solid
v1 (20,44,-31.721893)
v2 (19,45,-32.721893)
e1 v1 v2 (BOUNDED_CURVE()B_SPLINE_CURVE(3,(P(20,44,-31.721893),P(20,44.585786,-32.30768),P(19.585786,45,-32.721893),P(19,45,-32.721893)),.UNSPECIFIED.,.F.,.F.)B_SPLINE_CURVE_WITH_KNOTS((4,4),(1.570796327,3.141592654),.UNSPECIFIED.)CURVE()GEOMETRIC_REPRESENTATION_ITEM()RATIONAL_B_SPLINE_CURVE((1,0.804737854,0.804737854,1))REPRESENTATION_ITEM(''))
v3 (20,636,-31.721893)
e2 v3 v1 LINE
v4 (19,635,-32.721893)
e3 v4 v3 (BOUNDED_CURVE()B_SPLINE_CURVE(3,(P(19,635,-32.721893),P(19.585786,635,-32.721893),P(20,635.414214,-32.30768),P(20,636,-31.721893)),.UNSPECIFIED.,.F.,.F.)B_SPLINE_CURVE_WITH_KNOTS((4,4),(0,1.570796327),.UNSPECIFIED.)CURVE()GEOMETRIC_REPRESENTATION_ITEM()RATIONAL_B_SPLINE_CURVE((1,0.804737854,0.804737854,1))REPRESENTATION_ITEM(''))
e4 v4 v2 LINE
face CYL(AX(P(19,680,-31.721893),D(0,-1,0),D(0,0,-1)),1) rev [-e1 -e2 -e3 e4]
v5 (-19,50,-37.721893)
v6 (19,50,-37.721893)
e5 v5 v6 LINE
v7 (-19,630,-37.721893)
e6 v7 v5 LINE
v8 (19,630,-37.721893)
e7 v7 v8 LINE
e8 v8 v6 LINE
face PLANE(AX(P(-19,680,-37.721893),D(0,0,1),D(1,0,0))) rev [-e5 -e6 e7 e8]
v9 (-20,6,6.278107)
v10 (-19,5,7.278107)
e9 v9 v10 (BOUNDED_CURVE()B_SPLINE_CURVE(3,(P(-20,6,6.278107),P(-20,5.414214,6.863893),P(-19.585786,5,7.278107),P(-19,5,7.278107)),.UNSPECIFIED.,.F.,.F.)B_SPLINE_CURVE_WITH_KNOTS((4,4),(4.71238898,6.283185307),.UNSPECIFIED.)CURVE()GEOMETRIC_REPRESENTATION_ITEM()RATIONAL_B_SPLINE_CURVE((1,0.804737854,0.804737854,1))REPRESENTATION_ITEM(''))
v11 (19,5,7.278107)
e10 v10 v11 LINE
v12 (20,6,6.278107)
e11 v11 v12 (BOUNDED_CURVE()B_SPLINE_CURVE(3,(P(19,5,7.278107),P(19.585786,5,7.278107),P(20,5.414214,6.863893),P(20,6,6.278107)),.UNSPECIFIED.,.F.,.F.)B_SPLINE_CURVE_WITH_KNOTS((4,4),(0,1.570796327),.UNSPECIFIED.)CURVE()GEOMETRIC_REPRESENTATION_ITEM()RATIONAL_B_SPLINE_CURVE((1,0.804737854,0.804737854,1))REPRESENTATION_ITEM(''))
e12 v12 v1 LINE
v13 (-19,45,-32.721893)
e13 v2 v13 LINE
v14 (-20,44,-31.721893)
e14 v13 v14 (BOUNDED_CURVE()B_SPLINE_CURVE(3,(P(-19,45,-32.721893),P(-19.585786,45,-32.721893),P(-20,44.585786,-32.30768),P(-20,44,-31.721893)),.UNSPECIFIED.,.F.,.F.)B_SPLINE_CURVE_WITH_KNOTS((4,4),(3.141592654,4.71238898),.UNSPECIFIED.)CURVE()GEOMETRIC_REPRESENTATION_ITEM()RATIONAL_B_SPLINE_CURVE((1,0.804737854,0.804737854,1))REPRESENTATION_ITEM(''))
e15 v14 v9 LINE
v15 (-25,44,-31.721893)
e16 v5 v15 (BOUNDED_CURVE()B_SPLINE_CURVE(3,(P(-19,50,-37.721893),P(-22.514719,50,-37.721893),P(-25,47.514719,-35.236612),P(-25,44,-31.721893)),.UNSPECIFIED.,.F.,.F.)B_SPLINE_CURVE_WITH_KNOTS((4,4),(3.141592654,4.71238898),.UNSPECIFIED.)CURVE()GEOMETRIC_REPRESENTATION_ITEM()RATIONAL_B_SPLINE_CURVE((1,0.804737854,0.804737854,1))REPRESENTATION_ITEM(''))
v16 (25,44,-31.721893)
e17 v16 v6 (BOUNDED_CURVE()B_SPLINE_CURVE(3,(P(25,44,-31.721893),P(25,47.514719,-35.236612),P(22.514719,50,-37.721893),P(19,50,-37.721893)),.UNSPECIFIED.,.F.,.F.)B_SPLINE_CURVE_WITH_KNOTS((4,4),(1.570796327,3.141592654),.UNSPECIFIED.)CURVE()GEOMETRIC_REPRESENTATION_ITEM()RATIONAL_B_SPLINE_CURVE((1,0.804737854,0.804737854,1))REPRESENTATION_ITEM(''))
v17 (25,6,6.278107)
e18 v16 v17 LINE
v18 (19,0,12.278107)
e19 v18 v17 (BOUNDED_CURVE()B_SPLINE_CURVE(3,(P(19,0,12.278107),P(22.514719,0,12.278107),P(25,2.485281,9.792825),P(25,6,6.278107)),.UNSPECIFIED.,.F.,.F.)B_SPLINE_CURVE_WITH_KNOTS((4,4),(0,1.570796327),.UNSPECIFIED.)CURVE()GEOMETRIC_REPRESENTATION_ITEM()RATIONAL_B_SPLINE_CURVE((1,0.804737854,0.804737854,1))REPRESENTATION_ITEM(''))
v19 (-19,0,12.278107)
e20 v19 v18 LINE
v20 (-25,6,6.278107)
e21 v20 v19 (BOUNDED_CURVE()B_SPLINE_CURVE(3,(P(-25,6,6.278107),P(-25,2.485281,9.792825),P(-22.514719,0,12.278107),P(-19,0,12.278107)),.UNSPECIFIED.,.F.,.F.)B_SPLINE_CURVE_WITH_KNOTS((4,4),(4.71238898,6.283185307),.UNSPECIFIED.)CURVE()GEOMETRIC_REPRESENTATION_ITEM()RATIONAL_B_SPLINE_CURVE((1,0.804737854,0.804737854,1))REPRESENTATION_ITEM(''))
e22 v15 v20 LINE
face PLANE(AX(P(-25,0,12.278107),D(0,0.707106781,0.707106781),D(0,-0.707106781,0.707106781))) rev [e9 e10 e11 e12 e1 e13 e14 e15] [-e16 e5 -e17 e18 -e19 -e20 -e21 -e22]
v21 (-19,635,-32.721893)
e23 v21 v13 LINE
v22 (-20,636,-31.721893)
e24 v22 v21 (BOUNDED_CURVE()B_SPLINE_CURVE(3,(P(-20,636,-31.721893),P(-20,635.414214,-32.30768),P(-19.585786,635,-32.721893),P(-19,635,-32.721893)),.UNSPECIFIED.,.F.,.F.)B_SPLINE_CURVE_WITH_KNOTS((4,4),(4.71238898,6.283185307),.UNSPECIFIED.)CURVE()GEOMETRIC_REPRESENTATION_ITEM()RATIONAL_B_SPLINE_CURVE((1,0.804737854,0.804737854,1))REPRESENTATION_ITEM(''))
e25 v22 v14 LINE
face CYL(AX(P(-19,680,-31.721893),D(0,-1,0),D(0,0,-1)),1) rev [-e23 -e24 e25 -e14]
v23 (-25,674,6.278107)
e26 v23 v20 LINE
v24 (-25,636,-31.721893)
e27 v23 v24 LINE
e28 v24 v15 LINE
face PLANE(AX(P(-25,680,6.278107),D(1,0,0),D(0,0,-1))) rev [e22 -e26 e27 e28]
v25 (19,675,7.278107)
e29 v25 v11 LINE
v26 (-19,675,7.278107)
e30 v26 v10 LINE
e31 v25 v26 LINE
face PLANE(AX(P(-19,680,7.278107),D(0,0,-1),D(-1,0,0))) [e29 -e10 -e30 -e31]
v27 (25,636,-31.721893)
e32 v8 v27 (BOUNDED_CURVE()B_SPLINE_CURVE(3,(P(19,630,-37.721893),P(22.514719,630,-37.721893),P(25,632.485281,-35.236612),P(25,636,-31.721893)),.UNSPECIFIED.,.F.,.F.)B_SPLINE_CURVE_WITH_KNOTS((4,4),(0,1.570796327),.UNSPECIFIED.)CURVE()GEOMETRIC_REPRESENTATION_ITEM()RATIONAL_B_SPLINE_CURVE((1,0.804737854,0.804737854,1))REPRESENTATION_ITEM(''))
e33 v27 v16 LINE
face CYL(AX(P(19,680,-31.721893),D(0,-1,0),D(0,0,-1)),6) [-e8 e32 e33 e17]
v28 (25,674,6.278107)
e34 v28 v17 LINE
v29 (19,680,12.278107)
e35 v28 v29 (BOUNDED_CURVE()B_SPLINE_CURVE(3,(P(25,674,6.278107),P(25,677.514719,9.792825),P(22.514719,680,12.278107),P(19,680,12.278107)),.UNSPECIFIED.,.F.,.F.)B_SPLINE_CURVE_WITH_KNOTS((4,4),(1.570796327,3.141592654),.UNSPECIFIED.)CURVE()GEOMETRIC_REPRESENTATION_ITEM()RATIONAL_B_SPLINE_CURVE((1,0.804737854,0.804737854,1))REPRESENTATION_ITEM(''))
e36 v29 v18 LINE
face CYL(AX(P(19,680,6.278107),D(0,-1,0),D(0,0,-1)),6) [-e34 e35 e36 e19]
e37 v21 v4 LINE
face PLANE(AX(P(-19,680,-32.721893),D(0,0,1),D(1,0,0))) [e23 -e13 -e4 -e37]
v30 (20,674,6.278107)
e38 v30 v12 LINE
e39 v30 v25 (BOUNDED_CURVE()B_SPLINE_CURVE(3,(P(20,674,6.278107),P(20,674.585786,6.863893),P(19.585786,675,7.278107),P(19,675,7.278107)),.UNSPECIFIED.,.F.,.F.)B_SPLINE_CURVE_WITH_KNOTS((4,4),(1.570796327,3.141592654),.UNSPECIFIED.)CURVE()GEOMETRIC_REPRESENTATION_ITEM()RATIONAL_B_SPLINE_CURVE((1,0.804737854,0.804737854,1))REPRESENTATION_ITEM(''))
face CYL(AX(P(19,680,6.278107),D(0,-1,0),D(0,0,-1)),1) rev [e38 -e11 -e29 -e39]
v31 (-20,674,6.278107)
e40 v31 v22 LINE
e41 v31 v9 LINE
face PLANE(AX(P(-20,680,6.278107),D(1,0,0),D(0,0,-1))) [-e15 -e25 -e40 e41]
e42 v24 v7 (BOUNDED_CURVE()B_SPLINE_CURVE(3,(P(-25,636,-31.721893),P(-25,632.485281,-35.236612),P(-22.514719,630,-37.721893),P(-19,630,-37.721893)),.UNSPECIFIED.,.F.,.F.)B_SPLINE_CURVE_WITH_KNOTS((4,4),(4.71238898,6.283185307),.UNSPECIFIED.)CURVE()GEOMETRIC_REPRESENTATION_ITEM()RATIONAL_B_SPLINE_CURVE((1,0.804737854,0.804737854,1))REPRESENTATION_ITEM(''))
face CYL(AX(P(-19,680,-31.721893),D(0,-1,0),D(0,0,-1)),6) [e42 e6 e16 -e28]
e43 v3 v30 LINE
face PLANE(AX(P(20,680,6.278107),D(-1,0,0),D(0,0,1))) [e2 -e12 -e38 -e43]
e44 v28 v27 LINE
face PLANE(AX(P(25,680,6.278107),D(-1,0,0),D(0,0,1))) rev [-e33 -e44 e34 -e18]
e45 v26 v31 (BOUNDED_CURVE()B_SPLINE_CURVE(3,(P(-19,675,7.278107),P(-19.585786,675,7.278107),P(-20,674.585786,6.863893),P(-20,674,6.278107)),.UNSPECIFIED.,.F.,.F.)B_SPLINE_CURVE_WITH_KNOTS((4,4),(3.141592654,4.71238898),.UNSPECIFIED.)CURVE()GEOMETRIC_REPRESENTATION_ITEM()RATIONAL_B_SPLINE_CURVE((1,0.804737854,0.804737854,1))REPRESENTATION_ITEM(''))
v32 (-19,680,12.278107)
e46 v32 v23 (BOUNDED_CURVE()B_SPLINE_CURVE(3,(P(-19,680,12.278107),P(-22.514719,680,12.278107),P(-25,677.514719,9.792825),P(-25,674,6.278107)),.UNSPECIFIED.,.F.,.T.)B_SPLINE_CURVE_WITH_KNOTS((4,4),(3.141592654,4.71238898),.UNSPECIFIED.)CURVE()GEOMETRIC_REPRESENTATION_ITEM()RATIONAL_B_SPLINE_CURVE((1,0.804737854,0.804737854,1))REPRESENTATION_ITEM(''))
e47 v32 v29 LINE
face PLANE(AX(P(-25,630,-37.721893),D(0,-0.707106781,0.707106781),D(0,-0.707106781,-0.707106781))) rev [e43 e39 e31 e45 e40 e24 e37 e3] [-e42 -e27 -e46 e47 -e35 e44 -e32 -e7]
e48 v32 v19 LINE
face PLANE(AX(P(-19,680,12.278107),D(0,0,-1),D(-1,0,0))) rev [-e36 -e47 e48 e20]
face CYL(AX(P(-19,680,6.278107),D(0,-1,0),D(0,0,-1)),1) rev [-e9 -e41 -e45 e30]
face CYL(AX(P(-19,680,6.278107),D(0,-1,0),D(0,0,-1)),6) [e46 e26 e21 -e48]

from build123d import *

# Parameters (mm, degrees)
EXTRUDE_1_DEPTH     = 680
CUT_EXTRUDE_1_DEPTH = 683.878423476


with BuildPart() as part:
    # 草图1 → 凸台-拉伸1 (new body)
    with BuildSketch(Plane(origin=(0, 0, 0), x_dir=(1, 0, 0), z_dir=(0, 1, 0))):
        with BuildLine():
            Line((-19, -12.278106509), (19, -12.278106509))
            ThreePointArc((19, -12.278106509), (23.242640687, -10.520747196), (25, -6.278106509))
            Line((25, -6.278106509), (25, 31.721893491))
            ThreePointArc((25, 31.721893491), (23.242640687, 35.964534178), (19, 37.721893491))
            Line((19, 37.721893491), (-19, 37.721893491))
            ThreePointArc((-19, 37.721893491), (-23.242640687, 35.964534178), (-25, 31.721893491))
            Line((-25, 31.721893491), (-25, -6.278106509))
            ThreePointArc((-25, -6.278106509), (-23.242640687, -10.520747196), (-19, -12.278106509))
        make_face()
        with BuildLine():
            Line((-19, -7.278106509), (19, -7.278106509))
            ThreePointArc((19, -7.278106509), (19.707106781, -6.98521329), (20, -6.278106509))
            Line((20, -6.278106509), (20, 31.721893491))
            ThreePointArc((20, 31.721893491), (19.707106781, 32.429000272), (19, 32.721893491))
            Line((19, 32.721893491), (-19, 32.721893491))
            ThreePointArc((-19, 32.721893491), (-19.707106781, 32.429000272), (-20, 31.721893491))
            Line((-20, 31.721893491), (-20, -6.278106509))
            ThreePointArc((-20, -6.278106509), (-19.707106781, -6.98521329), (-19, -7.278106509))
        make_face(mode=Mode.SUBTRACT)
    extrude(amount=EXTRUDE_1_DEPTH)

    # 草图2 → 切除-拉伸1 (cut, through all)
    with BuildSketch(Plane(origin=(25, 0, 0), x_dir=(0, 0, -1), z_dir=(1, 0, 0))):
        Polygon((-12.278106509, 680), (37.721893491, 680), (37.721893491, 630), align=None)
        Polygon((-12.278106509, 0), (37.721893491, 50), (37.721893491, 0), align=None)
    extrude(amount=-CUT_EXTRUDE_1_DEPTH, mode=Mode.SUBTRACT)


solid = part.part
